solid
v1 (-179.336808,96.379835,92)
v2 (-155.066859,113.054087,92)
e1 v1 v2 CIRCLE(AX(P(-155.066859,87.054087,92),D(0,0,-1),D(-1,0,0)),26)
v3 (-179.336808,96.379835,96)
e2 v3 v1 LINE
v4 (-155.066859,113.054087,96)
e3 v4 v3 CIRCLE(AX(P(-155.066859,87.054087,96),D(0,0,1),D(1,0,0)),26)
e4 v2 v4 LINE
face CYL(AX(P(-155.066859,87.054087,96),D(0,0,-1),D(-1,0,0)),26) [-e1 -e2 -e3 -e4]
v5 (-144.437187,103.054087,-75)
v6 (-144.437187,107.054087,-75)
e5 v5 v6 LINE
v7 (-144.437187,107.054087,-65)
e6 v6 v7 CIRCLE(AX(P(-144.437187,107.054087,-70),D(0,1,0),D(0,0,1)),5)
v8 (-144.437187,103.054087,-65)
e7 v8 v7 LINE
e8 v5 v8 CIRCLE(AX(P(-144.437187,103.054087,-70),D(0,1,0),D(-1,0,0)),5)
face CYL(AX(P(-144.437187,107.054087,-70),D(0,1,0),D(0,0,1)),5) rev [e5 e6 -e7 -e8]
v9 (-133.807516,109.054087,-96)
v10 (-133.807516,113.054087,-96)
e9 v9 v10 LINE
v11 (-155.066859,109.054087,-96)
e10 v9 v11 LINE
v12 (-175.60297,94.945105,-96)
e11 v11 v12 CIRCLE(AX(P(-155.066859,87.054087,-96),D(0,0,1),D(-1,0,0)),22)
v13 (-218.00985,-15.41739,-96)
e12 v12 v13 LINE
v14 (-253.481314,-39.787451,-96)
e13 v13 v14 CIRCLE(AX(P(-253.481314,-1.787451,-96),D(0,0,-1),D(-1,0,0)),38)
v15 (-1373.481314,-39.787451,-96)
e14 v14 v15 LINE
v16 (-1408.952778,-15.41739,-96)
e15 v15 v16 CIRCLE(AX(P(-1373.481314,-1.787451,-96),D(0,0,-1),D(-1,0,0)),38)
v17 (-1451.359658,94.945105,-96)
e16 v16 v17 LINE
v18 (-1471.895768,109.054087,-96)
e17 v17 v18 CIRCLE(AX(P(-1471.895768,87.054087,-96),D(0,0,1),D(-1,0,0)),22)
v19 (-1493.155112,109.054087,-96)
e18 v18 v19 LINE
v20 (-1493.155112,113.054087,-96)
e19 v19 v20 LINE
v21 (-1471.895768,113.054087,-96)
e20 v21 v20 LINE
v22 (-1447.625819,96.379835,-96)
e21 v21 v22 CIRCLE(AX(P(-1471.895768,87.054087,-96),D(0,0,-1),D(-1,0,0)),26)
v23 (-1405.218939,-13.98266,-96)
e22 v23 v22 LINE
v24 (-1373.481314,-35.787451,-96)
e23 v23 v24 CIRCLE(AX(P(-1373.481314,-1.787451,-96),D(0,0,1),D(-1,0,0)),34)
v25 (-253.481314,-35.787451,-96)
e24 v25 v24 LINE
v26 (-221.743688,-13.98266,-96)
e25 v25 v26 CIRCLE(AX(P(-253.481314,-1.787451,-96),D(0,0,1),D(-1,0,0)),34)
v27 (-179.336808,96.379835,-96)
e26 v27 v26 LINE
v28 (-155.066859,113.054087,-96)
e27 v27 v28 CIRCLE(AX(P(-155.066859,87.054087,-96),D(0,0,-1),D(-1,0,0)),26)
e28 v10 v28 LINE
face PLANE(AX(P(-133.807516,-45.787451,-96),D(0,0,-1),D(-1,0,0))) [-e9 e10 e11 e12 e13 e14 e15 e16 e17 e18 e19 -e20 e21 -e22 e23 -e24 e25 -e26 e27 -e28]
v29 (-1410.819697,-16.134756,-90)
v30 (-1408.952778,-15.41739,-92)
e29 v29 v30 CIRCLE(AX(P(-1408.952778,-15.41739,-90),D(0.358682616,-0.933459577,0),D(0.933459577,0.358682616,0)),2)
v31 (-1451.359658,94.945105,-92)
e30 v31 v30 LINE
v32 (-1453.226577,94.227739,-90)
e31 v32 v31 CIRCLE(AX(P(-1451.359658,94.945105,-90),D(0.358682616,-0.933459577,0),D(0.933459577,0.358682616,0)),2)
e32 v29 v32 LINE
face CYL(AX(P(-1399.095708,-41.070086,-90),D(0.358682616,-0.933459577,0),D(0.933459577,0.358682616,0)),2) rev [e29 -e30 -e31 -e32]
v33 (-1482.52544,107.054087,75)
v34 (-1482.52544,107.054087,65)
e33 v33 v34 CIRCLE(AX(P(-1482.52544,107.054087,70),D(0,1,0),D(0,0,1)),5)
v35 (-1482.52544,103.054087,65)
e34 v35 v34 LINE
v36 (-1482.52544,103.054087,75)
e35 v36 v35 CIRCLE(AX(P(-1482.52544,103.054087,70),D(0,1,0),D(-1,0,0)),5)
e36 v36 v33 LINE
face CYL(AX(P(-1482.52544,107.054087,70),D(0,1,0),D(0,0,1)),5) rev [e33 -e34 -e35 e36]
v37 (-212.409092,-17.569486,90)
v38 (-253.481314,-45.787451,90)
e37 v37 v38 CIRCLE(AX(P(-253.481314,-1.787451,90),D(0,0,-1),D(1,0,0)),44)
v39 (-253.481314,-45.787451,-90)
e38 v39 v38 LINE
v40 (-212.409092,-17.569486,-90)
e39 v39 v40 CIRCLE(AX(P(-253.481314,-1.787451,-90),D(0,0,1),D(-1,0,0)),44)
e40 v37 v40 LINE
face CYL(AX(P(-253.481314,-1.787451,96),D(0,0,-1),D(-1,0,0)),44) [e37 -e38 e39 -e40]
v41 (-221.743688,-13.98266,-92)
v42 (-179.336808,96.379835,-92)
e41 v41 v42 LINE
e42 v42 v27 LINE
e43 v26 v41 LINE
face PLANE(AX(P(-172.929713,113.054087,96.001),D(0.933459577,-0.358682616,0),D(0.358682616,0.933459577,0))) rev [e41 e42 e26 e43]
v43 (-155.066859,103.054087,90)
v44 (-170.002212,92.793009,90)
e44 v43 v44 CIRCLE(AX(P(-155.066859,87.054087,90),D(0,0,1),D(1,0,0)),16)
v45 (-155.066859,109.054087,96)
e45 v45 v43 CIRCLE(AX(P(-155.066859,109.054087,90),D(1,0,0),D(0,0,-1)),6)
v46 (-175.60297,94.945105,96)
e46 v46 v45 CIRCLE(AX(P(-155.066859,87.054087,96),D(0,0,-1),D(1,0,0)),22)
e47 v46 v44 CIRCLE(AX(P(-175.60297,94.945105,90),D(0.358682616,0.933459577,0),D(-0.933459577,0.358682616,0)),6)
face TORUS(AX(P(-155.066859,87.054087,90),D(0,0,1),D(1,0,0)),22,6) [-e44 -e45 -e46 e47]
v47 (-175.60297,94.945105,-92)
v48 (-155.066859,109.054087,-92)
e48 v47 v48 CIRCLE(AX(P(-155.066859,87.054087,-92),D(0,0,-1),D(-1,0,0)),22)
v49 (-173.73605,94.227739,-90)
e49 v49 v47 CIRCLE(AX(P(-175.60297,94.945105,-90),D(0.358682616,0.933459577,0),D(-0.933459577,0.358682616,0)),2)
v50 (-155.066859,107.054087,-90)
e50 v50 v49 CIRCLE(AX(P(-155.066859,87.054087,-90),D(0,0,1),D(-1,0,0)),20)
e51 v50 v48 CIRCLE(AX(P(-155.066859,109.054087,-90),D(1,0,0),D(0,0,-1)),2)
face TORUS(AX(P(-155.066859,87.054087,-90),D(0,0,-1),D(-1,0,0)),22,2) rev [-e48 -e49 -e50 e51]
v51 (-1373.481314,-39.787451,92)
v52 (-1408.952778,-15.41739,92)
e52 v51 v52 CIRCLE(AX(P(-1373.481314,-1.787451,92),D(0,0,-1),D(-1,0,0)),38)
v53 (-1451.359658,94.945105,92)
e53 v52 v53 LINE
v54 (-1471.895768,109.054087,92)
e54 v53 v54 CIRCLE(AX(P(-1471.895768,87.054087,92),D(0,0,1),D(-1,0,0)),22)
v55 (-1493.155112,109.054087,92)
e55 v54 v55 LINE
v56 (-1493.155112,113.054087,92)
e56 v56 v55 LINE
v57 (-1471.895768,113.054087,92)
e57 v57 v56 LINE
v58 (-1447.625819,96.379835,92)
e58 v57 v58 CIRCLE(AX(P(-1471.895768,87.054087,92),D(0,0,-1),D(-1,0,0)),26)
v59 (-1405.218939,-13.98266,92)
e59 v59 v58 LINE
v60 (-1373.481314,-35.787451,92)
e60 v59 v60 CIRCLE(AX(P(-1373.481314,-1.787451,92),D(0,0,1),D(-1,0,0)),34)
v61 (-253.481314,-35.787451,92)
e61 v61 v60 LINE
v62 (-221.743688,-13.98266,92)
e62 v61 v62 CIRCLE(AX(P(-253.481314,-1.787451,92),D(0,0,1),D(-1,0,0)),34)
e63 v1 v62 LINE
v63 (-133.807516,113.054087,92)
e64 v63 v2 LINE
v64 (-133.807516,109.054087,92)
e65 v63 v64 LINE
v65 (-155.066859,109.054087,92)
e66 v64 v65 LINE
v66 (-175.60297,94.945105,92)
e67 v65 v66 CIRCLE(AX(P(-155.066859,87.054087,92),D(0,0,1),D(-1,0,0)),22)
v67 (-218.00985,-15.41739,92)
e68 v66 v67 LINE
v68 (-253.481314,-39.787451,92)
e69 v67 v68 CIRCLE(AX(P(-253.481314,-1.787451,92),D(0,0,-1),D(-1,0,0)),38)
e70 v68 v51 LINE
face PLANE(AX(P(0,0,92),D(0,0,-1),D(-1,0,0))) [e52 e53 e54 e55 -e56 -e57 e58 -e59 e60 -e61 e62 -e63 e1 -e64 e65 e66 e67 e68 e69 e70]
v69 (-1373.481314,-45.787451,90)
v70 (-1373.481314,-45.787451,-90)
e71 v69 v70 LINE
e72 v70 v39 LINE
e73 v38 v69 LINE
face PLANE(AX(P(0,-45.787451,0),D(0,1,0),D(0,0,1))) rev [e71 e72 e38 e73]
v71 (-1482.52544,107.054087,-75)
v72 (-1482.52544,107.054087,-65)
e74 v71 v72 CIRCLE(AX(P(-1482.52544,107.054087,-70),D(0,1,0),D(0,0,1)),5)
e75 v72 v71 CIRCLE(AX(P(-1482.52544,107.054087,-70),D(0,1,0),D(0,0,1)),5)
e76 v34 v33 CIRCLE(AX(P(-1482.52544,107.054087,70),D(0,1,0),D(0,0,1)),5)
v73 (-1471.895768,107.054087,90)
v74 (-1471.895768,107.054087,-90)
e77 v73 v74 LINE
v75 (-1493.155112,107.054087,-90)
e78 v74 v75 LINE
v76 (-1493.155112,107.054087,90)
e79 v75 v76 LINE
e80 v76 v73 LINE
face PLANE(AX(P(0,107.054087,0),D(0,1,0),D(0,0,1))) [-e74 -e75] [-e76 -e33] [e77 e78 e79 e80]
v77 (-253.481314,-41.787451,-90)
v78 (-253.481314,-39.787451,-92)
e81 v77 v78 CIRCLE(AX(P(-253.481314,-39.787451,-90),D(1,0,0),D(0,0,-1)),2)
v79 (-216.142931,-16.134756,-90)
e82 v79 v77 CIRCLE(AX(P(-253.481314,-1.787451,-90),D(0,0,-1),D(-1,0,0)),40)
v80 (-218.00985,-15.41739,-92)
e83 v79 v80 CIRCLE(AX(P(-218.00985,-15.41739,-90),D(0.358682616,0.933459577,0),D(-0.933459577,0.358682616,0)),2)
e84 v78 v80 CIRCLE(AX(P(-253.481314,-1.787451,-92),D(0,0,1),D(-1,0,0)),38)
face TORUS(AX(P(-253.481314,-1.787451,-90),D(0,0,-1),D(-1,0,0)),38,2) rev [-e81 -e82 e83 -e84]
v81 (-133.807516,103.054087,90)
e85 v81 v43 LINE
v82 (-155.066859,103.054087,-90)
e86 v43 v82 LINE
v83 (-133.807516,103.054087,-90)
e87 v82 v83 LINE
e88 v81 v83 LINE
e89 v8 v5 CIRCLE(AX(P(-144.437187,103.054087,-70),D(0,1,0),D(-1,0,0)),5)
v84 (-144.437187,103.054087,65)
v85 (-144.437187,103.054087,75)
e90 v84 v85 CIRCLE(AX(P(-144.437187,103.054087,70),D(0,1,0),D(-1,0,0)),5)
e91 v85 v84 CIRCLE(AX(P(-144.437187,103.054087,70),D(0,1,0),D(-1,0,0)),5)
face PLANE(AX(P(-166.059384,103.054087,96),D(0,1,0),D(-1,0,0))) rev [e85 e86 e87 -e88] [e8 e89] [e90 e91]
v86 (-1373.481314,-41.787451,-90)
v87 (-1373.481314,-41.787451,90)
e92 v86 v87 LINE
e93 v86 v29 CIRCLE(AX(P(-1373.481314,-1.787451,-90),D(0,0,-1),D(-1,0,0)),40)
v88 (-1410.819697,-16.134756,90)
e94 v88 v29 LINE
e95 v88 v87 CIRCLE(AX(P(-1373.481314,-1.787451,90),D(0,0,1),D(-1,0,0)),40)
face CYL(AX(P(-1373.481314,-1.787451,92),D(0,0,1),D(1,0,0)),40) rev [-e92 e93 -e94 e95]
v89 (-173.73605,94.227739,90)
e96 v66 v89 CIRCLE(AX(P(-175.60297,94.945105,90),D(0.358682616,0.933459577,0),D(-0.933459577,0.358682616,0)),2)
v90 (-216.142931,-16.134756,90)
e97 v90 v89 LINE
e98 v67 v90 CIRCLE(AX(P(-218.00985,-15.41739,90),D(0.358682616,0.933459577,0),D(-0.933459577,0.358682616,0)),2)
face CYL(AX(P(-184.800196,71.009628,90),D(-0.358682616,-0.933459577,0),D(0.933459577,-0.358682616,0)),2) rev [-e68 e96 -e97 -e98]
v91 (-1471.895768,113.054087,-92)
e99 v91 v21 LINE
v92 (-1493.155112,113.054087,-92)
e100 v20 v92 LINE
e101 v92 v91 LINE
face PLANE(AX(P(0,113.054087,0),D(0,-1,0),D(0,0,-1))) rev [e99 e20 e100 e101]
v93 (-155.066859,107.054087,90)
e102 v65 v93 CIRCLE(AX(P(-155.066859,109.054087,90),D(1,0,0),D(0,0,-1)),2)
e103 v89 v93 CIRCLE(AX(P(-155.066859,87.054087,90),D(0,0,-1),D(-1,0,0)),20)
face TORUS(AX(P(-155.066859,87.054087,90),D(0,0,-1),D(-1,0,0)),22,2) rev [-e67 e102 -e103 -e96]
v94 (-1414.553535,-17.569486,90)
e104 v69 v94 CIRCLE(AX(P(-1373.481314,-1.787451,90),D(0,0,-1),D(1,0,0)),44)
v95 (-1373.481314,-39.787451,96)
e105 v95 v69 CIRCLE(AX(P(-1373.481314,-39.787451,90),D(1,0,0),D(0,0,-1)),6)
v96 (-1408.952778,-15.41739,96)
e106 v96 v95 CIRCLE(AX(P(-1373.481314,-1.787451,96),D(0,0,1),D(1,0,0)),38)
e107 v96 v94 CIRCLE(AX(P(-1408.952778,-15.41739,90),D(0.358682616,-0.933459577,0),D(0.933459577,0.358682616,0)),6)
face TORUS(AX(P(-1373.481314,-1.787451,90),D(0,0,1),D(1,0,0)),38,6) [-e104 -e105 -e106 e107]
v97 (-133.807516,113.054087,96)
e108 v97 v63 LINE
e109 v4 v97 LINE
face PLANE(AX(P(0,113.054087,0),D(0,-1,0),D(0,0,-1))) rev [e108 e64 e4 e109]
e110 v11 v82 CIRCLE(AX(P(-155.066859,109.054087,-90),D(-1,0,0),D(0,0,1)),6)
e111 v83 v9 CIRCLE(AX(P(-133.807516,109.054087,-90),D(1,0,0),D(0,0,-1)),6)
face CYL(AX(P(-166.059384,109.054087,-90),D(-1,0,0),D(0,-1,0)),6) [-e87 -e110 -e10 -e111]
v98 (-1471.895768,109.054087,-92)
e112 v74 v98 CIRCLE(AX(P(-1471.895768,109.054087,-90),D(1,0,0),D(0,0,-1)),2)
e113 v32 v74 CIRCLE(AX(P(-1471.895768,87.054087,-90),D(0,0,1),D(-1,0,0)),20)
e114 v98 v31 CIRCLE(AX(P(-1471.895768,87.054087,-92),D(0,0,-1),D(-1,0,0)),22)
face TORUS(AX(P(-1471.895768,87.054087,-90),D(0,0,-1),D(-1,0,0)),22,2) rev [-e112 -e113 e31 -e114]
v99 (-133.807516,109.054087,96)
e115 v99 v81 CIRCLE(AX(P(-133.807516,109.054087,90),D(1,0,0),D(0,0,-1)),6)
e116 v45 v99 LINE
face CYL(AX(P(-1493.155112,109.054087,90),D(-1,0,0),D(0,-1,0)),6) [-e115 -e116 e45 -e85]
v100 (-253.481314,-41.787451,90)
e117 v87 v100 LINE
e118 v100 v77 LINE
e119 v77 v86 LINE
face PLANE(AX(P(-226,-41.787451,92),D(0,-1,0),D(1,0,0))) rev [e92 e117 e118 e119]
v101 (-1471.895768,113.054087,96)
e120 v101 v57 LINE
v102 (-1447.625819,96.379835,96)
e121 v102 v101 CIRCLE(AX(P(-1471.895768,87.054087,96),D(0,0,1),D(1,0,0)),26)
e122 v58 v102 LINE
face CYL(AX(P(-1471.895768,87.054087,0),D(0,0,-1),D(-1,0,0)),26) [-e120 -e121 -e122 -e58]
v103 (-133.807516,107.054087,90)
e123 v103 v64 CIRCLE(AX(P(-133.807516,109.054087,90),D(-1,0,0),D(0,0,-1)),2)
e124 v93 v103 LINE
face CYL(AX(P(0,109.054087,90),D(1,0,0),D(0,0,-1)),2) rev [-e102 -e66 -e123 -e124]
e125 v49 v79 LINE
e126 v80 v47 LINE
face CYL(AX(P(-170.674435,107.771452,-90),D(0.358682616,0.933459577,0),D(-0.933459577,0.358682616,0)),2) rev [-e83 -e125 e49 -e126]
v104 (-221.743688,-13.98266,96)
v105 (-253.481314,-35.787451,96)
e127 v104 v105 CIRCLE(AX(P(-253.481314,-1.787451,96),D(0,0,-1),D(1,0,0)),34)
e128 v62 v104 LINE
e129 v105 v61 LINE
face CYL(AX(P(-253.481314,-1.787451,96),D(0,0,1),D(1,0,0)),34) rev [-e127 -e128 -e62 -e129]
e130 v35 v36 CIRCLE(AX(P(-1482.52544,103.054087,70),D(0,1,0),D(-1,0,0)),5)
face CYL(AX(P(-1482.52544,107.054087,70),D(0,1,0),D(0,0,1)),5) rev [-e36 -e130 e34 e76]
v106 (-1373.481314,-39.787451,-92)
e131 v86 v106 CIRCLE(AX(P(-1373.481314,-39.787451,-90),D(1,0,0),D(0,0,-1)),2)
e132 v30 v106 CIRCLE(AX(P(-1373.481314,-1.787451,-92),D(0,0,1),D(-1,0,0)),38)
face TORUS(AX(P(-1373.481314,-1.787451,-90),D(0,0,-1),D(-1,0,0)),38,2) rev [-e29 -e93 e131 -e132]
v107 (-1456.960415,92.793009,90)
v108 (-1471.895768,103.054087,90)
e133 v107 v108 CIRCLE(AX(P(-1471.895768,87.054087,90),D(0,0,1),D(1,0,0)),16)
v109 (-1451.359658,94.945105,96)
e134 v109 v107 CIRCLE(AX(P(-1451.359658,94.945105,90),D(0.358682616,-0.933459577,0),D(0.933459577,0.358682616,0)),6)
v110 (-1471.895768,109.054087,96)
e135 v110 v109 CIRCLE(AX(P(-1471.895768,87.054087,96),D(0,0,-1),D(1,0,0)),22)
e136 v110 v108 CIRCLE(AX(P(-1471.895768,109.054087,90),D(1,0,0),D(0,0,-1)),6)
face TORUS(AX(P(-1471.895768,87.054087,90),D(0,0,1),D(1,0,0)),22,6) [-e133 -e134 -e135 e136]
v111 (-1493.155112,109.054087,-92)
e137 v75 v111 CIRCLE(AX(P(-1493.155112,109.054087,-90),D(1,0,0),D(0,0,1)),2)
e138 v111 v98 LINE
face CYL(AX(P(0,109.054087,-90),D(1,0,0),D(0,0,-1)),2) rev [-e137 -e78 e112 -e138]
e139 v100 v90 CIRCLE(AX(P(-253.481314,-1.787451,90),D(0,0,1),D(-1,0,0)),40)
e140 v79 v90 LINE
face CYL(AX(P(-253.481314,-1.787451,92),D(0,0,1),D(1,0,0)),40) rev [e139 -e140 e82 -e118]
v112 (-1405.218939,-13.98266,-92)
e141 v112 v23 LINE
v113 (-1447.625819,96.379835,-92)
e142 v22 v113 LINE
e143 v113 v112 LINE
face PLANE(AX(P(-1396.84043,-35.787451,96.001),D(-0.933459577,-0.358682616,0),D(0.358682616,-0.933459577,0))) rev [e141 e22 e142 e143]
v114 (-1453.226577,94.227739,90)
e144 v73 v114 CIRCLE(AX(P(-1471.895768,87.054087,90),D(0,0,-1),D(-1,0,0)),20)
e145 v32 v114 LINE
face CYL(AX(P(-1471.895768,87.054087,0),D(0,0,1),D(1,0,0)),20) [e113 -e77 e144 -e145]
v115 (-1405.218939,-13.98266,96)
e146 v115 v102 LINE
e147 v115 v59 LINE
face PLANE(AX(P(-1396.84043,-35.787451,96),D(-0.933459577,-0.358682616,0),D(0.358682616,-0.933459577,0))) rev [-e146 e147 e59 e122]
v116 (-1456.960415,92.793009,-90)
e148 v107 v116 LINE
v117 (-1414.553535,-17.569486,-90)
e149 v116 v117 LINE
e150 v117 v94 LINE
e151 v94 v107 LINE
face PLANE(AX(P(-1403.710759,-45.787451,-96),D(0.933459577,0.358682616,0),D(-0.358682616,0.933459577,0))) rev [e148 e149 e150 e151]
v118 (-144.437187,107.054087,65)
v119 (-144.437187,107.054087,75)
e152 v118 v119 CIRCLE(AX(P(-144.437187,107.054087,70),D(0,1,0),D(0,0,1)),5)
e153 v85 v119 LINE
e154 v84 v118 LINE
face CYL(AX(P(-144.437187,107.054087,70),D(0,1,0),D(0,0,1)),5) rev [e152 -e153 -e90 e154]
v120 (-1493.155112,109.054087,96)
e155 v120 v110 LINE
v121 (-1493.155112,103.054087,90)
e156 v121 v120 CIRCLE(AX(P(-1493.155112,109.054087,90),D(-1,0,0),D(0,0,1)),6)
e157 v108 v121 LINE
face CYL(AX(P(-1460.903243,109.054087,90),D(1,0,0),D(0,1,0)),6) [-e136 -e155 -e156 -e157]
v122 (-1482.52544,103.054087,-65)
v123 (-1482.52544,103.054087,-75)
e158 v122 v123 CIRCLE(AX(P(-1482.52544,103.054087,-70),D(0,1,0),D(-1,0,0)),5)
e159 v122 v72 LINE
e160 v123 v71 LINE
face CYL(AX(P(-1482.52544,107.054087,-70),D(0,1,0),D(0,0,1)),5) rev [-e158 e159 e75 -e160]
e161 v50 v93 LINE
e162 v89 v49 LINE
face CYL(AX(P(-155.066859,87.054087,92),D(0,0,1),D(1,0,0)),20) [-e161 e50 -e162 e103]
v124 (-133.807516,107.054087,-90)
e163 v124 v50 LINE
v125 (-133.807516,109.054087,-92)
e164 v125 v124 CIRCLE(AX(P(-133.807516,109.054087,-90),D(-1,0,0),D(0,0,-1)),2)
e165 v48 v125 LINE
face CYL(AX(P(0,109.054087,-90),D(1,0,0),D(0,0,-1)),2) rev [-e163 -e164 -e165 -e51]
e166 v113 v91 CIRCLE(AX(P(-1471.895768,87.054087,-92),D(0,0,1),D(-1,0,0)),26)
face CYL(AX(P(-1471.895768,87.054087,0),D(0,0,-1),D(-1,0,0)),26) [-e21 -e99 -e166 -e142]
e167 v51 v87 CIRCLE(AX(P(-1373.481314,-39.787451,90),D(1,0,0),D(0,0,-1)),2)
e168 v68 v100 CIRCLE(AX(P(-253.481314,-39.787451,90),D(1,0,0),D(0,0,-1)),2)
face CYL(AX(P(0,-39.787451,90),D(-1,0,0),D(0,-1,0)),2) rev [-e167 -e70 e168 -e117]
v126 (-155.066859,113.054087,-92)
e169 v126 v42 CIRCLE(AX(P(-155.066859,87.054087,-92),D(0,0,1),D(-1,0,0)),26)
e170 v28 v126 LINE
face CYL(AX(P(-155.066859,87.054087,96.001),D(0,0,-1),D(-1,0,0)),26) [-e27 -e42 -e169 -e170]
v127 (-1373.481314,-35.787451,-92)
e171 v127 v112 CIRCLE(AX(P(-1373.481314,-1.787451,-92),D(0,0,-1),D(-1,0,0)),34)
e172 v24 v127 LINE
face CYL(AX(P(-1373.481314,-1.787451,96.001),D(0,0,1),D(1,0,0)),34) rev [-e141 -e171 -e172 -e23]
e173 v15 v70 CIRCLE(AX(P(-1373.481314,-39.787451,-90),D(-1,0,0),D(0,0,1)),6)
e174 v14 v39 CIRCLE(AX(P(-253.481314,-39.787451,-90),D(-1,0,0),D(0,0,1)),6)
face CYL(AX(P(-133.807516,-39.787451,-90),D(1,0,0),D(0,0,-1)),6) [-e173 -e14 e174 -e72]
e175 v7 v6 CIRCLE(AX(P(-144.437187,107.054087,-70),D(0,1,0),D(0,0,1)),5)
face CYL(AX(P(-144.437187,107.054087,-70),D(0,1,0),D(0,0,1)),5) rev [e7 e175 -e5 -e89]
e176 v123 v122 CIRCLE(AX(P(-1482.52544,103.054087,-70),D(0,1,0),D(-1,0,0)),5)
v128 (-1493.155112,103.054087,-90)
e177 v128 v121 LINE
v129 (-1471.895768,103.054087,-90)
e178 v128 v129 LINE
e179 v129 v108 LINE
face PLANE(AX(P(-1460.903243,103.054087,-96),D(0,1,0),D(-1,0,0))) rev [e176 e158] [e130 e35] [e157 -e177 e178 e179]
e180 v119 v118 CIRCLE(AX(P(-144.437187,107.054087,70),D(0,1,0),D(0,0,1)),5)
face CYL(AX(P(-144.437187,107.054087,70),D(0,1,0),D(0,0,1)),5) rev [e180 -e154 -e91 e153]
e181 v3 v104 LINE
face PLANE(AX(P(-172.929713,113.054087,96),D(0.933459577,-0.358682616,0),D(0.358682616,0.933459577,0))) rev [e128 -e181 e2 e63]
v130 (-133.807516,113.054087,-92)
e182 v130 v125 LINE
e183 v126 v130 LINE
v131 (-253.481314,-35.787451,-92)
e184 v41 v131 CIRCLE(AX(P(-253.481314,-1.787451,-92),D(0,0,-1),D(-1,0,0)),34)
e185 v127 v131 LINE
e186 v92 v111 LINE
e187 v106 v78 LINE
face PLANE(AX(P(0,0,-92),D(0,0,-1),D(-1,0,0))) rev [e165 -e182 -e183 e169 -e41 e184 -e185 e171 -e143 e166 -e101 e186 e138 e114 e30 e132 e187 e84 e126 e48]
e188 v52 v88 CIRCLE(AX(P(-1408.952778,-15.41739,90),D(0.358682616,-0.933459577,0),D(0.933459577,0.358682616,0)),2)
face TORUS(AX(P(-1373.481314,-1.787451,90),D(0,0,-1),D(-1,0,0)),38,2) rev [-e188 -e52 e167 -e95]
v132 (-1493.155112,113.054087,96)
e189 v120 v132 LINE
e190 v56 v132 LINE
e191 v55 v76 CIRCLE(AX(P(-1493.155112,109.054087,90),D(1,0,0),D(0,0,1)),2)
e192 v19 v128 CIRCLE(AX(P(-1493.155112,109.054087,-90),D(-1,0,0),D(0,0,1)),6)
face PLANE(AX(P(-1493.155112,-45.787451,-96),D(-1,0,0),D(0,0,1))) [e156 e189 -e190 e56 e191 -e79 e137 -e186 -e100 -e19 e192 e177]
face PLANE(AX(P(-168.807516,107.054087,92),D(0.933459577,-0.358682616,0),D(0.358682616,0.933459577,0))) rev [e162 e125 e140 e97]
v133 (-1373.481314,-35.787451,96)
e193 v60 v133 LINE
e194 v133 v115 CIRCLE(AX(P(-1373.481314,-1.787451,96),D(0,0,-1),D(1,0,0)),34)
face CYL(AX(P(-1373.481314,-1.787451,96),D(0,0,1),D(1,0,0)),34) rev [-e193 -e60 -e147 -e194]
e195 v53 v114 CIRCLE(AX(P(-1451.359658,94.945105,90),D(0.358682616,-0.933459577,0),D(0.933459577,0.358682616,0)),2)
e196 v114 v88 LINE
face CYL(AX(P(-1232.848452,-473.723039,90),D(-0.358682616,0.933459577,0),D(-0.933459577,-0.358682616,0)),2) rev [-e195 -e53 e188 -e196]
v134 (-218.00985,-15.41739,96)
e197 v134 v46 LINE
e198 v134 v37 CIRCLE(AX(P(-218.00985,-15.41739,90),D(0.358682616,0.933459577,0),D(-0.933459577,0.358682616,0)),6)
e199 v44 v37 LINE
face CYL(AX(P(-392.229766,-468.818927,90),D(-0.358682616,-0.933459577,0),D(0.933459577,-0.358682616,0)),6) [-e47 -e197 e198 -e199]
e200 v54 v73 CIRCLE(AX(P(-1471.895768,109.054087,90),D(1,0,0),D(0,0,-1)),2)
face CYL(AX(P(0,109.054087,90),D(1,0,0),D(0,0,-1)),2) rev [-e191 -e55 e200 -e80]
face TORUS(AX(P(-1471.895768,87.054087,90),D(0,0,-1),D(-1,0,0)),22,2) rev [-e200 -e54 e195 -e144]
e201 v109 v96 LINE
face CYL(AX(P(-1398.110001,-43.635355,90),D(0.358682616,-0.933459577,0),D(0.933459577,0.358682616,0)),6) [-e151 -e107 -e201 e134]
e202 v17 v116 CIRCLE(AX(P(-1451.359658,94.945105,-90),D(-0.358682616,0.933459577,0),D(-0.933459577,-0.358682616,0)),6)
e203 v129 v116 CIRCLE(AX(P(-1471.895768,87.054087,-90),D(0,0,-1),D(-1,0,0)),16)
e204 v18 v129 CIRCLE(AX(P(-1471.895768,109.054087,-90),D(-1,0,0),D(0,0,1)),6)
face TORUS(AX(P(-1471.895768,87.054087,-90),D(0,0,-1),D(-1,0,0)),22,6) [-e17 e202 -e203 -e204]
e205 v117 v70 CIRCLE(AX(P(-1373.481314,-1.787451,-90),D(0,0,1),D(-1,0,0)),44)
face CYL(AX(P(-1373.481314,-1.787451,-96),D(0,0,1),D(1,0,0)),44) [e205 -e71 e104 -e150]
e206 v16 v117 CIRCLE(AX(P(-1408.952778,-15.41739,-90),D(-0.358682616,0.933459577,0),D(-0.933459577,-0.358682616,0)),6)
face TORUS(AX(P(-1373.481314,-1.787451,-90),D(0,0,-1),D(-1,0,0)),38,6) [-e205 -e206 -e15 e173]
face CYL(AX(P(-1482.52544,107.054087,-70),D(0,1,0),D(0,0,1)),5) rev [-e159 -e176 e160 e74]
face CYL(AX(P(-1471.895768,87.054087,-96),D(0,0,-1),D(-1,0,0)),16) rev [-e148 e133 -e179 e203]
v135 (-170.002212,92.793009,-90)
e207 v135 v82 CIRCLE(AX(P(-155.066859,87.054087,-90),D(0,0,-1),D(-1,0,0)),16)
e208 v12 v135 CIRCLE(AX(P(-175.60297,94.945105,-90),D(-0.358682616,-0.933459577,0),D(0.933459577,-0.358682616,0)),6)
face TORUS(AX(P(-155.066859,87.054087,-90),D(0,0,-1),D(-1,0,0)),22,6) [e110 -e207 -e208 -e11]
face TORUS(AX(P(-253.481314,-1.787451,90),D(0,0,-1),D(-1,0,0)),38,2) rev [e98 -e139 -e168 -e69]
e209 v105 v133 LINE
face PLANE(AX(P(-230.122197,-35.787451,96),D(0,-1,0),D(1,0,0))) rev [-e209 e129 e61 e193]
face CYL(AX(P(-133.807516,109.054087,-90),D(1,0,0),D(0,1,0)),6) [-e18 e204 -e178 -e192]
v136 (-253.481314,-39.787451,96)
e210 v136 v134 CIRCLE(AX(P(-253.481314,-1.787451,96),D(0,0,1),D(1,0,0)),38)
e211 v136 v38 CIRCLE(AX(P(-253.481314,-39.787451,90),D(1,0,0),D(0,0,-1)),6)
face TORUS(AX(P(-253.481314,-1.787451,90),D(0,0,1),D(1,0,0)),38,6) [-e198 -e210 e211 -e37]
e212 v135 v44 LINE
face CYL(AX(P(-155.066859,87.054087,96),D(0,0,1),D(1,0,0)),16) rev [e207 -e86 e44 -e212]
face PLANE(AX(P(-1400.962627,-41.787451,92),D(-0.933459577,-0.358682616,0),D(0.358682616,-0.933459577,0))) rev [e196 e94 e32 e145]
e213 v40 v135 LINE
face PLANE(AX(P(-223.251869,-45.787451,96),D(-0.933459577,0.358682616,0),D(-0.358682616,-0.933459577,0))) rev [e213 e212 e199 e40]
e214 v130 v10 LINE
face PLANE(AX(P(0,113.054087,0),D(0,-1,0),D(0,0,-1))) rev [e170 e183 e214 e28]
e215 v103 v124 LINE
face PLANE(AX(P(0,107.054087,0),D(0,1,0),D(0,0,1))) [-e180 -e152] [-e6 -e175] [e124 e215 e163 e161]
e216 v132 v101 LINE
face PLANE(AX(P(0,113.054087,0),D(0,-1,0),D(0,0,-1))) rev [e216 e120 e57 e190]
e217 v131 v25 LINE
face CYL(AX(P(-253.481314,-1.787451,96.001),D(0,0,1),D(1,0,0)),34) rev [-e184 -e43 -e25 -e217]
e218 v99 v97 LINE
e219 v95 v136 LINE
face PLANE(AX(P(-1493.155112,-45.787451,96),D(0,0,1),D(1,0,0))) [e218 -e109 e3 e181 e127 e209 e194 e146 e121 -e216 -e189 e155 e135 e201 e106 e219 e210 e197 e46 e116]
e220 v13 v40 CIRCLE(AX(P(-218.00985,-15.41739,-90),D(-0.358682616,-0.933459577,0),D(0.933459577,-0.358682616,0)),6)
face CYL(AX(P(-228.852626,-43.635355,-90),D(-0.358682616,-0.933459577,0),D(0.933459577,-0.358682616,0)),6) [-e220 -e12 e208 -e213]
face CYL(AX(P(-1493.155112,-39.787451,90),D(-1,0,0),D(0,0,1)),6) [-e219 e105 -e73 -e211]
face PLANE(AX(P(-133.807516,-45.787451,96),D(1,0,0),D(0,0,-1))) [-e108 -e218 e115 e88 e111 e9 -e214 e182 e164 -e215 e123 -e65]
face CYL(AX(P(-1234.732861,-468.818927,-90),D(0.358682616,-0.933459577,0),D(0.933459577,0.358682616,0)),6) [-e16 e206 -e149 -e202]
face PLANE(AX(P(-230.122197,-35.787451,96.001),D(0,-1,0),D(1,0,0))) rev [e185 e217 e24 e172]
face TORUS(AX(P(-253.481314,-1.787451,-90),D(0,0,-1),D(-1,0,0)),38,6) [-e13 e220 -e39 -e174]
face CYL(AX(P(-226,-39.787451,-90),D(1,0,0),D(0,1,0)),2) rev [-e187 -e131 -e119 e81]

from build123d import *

# Parameters (mm, degrees)
SKETCH1_W                      = 1359.347595865
SKETCH1_H                      = 192
BOSS_EXTRUDE1_DEPTH            = 152.841538075
CUT_EXTRUDE1_DEPTH             = 184
SKETCH3_W                      = 1359.347595865
SKETCH3_H                      = 4
BOSS_EXTRUDE2_DEPTH            = 6
SKETCH4_W                      = 1359.347595865
SKETCH4_H                      = 4
BOSS_EXTRUDE3_DEPTH            = 6
CUT_EXTRUDE2_DEPTH             = 1510.687853091
CUT_EXTRUDE3_REACH             = 1511.688
CUT_EXTRUDE4_DEPTH             = 1510.687853091
CUT_EXTRUDE5_DEPTH             = 1510.184353805
F_10_0_10_DIAMETER_HOLE1_D     = 10
F_10_0_10_DIAMETER_HOLE1_DEPTH = 152.841538075
FILLET1_R                      = 34.000000002
FILLET2_R                      = 16
FILLET3_R                      = 20
FILLET4_R                      = 40.000000002
FILLET5_R                      = 44.000000002
FILLET6_R                      = 2
FILLET7_R                      = 6
FILLET8_R                      = 26


with BuildPart() as part:
    # Sketch1 → Boss-Extrude1 (new body)
    with BuildSketch(Plane(origin=(0, 107.054087174, 0), x_dir=(1, 0, 0), z_dir=(0, 1, 0))):
        with Locations((-813.481313616, 0)):
            Rectangle(SKETCH1_W, SKETCH1_H)
    extrude(amount=-BOSS_EXTRUDE1_DEPTH)

    # Sketch2 → Cut-Extrude1 (cut)
    with BuildSketch(Plane(origin=(0, 0, -92), x_dir=(-1, 0, 0), z_dir=(0, 0, -1))):
        Polygon((168.807515683, 107.054087174), (226, -41.787450901), (1400.962627231, -41.787450901), (1458.155111548, 107.054087174), align=None)
    extrude(amount=-CUT_EXTRUDE1_DEPTH, mode=Mode.SUBTRACT)

    # Sketch3 → Boss-Extrude2 (add)
    with BuildSketch(Plane(origin=(0, 107.054087174, 0), x_dir=(-1, 0, 0), z_dir=(0, 1, 0))):
        with Locations((813.481313616, -94)):
            Rectangle(SKETCH3_W, SKETCH3_H)
    extrude(amount=BOSS_EXTRUDE2_DEPTH)

    # Sketch4 → Boss-Extrude3 (add)
    with BuildSketch(Plane(origin=(0, 107.054087174, 0), x_dir=(-1, 0, 0), z_dir=(0, 1, 0))):
        with Locations((813.481313616, 94)):
            Rectangle(SKETCH4_W, SKETCH4_H)
    extrude(amount=BOSS_EXTRUDE3_DEPTH)

    # Sketch5 → Cut-Extrude2 (cut, through all)
    with BuildSketch(Plane(origin=(0, 0, -96), x_dir=(-1, 0, 0), z_dir=(0, 0, -1))):
        Polygon((166.059384321, 103.054087174), (133.807515683, 103.054087174), (133.807515683, -45.787450901), (223.251868638, -45.787450901), align=None)
    extrude(amount=-CUT_EXTRUDE2_DEPTH, mode=Mode.SUBTRACT)

    # Sketch6 → Cut-Extrude3 (cut, up to next)
    with BuildSketch(Plane(origin=(0, 0, -96), x_dir=(-1, 0, 0), z_dir=(0, 0, -1)), mode=Mode.PRIVATE) as cut_extrude3_sk1:
        Polygon((1454.032914506, 113.054087174), (172.929712725, 113.054087174), (230.122197042, -35.787450901), (1396.840430189, -35.787450901), align=None)
    cut_extrude3_tool1 = extrude(cut_extrude3_sk1.sketch, amount=-CUT_EXTRUDE3_REACH, mode=Mode.PRIVATE) & part.part
    add(cut_extrude3_tool1.solids().sort_by_distance((-813.481314, 39.792528, -96))[0], mode=Mode.SUBTRACT)

    # Sketch7 → Cut-Extrude4 (cut, through all)
    with BuildSketch(Plane.XY.offset(96)):
        Polygon((-1460.90324291, 103.054087174), (-1493.155111548, 103.054087174), (-1493.155111548, -45.787450901), (-1403.710758593, -45.787450901), align=None)
    extrude(amount=-CUT_EXTRUDE4_DEPTH, mode=Mode.SUBTRACT)

    # Sketch8 → Cut-Extrude5 (cut, through all)
    with BuildSketch(Plane(origin=(0, 0, 92), x_dir=(-1, 0, 0), z_dir=(0, 0, -1))):
        Polygon((1454.032914506, 113.054087174), (172.929712725, 113.054087174), (230.122197042, -35.787450901), (1396.840430189, -35.787450901), align=None)
    extrude(amount=-CUT_EXTRUDE5_DEPTH, mode=Mode.SUBTRACT)

    # Ø10.0 (10) Diameter Hole1
    with Locations(Plane(origin=(0, 107.054087174, 0), x_dir=(1, 0, 0), z_dir=(0, 1, 0))):
        with Locations((-144.437187279, 70), (-144.437187279, -70), (-1482.525439952, 70), (-1482.525439952, -70)):
            Hole(F_10_0_10_DIAMETER_HOLE1_D / 2, depth=F_10_0_10_DIAMETER_HOLE1_DEPTH)

    # Fillet1
    fillet1_edges = [part.edges().sort_by_distance(p)[0] for p in [
        (-1396.840430189, -35.787450901, 94),
        (-230.122197042, -35.787450901, 94),
        (-230.122197042, -35.787450901, -94),
        (-1396.840430189, -35.787450901, -94),
    ]]
    fillet(fillet1_edges, radius=FILLET1_R)

    # Fillet2
    fillet2_edges = [part.edges().sort_by_distance(p)[0] for p in [
        (-166.059384321, 103.054087174, 0),
        (-1460.90324291, 103.054087174, 0),
    ]]
    fillet(fillet2_edges, radius=FILLET2_R)

    # Fillet3
    fillet3_edges = [part.edges().sort_by_distance(p)[0] for p in [
        (-168.807515683, 107.054087174, 0),
        (-1458.155111548, 107.054087174, 0),
    ]]
    fillet(fillet3_edges, radius=FILLET3_R)

    # Fillet4
    fillet4_edges = [part.edges().sort_by_distance(p)[0] for p in [
        (-1400.962627231, -41.787450901, 0),
        (-226, -41.787450901, 0),
    ]]
    fillet(fillet4_edges, radius=FILLET4_R)

    # Fillet5
    fillet5_edges = [part.edges().sort_by_distance(p)[0] for p in [
        (-223.251868638, -45.787450901, 0),
        (-1403.710758593, -45.787450901, 0),
    ]]
    fillet(fillet5_edges, radius=FILLET5_R)

    # Fillet6
    fillet6_edges = [part.edges().sort_by_distance(p)[0] for p in [
        (-194.939490479, 39.04649198, -92),
        (-194.939490479, 39.04649198, 92),
        (-144.437187279, 107.054087174, -92),
        (-1482.525439952, 107.054087174, 92),
        (-166.39220553, 103.538519925, -92),
        (-166.39220553, 103.538519925, 92),
        (-1460.570421701, 103.538519925, -92),
        (-1460.570421701, 103.538519925, 92),
        (-1432.023136753, 39.04649198, -92),
        (-1432.023136753, 39.04649198, 92),
        (-813.481313616, -41.787450901, -92),
        (-230.830620305, -34.756316403, -92),
        (-1396.132006926, -34.756316403, -92),
        (-813.481313616, -41.787450901, 92),
        (-230.830620305, -34.756316403, 92),
        (-1396.132006926, -34.756316403, 92),
        (-1482.525439952, 107.054087174, -92),
        (-144.437187279, 107.054087174, 92),
    ]]
    fillet(fillet6_edges, radius=FILLET6_R)

    # Fillet7
    fillet7_edges = [part.edges().sort_by_distance(p)[0] for p in [
        (-144.437187279, 103.054087174, -96),
        (-144.437187279, 103.054087174, 96),
        (-1482.525439952, 103.054087174, 96),
        (-1482.525439952, 103.054087174, -96),
        (-164.127136199, 100.241633375, -96),
        (-164.127136199, 100.241633375, 96),
        (-1462.835491032, 100.241633375, 96),
        (-1462.835491032, 100.241633375, -96),
        (-1435.756975059, 37.611761518, 96),
        (-1435.756975059, 37.611761518, -96),
        (-813.481313616, -45.787450901, 96),
        (-191.205652172, 37.611761518, 96),
        (-228.565550974, -38.053202954, 96),
        (-1398.397076257, -38.053202954, 96),
        (-813.481313616, -45.787450901, -96),
        (-191.205652172, 37.611761518, -96),
        (-228.565550974, -38.053202954, -96),
        (-1398.397076257, -38.053202954, -96),
    ]]
    fillet(fillet7_edges, radius=FILLET7_R)

    # Fillet8
    fillet8_edges = [part.edges().sort_by_distance(p)[0] for p in [
        (-1454.032914506, 113.054087174, 94),
        (-172.929712725, 113.054087174, 94),
        (-172.929712725, 113.054087174, -94),
        (-1454.032914506, 113.054087174, -94),
    ]]
    fillet(fillet8_edges, radius=FILLET8_R)


solid = part.part
